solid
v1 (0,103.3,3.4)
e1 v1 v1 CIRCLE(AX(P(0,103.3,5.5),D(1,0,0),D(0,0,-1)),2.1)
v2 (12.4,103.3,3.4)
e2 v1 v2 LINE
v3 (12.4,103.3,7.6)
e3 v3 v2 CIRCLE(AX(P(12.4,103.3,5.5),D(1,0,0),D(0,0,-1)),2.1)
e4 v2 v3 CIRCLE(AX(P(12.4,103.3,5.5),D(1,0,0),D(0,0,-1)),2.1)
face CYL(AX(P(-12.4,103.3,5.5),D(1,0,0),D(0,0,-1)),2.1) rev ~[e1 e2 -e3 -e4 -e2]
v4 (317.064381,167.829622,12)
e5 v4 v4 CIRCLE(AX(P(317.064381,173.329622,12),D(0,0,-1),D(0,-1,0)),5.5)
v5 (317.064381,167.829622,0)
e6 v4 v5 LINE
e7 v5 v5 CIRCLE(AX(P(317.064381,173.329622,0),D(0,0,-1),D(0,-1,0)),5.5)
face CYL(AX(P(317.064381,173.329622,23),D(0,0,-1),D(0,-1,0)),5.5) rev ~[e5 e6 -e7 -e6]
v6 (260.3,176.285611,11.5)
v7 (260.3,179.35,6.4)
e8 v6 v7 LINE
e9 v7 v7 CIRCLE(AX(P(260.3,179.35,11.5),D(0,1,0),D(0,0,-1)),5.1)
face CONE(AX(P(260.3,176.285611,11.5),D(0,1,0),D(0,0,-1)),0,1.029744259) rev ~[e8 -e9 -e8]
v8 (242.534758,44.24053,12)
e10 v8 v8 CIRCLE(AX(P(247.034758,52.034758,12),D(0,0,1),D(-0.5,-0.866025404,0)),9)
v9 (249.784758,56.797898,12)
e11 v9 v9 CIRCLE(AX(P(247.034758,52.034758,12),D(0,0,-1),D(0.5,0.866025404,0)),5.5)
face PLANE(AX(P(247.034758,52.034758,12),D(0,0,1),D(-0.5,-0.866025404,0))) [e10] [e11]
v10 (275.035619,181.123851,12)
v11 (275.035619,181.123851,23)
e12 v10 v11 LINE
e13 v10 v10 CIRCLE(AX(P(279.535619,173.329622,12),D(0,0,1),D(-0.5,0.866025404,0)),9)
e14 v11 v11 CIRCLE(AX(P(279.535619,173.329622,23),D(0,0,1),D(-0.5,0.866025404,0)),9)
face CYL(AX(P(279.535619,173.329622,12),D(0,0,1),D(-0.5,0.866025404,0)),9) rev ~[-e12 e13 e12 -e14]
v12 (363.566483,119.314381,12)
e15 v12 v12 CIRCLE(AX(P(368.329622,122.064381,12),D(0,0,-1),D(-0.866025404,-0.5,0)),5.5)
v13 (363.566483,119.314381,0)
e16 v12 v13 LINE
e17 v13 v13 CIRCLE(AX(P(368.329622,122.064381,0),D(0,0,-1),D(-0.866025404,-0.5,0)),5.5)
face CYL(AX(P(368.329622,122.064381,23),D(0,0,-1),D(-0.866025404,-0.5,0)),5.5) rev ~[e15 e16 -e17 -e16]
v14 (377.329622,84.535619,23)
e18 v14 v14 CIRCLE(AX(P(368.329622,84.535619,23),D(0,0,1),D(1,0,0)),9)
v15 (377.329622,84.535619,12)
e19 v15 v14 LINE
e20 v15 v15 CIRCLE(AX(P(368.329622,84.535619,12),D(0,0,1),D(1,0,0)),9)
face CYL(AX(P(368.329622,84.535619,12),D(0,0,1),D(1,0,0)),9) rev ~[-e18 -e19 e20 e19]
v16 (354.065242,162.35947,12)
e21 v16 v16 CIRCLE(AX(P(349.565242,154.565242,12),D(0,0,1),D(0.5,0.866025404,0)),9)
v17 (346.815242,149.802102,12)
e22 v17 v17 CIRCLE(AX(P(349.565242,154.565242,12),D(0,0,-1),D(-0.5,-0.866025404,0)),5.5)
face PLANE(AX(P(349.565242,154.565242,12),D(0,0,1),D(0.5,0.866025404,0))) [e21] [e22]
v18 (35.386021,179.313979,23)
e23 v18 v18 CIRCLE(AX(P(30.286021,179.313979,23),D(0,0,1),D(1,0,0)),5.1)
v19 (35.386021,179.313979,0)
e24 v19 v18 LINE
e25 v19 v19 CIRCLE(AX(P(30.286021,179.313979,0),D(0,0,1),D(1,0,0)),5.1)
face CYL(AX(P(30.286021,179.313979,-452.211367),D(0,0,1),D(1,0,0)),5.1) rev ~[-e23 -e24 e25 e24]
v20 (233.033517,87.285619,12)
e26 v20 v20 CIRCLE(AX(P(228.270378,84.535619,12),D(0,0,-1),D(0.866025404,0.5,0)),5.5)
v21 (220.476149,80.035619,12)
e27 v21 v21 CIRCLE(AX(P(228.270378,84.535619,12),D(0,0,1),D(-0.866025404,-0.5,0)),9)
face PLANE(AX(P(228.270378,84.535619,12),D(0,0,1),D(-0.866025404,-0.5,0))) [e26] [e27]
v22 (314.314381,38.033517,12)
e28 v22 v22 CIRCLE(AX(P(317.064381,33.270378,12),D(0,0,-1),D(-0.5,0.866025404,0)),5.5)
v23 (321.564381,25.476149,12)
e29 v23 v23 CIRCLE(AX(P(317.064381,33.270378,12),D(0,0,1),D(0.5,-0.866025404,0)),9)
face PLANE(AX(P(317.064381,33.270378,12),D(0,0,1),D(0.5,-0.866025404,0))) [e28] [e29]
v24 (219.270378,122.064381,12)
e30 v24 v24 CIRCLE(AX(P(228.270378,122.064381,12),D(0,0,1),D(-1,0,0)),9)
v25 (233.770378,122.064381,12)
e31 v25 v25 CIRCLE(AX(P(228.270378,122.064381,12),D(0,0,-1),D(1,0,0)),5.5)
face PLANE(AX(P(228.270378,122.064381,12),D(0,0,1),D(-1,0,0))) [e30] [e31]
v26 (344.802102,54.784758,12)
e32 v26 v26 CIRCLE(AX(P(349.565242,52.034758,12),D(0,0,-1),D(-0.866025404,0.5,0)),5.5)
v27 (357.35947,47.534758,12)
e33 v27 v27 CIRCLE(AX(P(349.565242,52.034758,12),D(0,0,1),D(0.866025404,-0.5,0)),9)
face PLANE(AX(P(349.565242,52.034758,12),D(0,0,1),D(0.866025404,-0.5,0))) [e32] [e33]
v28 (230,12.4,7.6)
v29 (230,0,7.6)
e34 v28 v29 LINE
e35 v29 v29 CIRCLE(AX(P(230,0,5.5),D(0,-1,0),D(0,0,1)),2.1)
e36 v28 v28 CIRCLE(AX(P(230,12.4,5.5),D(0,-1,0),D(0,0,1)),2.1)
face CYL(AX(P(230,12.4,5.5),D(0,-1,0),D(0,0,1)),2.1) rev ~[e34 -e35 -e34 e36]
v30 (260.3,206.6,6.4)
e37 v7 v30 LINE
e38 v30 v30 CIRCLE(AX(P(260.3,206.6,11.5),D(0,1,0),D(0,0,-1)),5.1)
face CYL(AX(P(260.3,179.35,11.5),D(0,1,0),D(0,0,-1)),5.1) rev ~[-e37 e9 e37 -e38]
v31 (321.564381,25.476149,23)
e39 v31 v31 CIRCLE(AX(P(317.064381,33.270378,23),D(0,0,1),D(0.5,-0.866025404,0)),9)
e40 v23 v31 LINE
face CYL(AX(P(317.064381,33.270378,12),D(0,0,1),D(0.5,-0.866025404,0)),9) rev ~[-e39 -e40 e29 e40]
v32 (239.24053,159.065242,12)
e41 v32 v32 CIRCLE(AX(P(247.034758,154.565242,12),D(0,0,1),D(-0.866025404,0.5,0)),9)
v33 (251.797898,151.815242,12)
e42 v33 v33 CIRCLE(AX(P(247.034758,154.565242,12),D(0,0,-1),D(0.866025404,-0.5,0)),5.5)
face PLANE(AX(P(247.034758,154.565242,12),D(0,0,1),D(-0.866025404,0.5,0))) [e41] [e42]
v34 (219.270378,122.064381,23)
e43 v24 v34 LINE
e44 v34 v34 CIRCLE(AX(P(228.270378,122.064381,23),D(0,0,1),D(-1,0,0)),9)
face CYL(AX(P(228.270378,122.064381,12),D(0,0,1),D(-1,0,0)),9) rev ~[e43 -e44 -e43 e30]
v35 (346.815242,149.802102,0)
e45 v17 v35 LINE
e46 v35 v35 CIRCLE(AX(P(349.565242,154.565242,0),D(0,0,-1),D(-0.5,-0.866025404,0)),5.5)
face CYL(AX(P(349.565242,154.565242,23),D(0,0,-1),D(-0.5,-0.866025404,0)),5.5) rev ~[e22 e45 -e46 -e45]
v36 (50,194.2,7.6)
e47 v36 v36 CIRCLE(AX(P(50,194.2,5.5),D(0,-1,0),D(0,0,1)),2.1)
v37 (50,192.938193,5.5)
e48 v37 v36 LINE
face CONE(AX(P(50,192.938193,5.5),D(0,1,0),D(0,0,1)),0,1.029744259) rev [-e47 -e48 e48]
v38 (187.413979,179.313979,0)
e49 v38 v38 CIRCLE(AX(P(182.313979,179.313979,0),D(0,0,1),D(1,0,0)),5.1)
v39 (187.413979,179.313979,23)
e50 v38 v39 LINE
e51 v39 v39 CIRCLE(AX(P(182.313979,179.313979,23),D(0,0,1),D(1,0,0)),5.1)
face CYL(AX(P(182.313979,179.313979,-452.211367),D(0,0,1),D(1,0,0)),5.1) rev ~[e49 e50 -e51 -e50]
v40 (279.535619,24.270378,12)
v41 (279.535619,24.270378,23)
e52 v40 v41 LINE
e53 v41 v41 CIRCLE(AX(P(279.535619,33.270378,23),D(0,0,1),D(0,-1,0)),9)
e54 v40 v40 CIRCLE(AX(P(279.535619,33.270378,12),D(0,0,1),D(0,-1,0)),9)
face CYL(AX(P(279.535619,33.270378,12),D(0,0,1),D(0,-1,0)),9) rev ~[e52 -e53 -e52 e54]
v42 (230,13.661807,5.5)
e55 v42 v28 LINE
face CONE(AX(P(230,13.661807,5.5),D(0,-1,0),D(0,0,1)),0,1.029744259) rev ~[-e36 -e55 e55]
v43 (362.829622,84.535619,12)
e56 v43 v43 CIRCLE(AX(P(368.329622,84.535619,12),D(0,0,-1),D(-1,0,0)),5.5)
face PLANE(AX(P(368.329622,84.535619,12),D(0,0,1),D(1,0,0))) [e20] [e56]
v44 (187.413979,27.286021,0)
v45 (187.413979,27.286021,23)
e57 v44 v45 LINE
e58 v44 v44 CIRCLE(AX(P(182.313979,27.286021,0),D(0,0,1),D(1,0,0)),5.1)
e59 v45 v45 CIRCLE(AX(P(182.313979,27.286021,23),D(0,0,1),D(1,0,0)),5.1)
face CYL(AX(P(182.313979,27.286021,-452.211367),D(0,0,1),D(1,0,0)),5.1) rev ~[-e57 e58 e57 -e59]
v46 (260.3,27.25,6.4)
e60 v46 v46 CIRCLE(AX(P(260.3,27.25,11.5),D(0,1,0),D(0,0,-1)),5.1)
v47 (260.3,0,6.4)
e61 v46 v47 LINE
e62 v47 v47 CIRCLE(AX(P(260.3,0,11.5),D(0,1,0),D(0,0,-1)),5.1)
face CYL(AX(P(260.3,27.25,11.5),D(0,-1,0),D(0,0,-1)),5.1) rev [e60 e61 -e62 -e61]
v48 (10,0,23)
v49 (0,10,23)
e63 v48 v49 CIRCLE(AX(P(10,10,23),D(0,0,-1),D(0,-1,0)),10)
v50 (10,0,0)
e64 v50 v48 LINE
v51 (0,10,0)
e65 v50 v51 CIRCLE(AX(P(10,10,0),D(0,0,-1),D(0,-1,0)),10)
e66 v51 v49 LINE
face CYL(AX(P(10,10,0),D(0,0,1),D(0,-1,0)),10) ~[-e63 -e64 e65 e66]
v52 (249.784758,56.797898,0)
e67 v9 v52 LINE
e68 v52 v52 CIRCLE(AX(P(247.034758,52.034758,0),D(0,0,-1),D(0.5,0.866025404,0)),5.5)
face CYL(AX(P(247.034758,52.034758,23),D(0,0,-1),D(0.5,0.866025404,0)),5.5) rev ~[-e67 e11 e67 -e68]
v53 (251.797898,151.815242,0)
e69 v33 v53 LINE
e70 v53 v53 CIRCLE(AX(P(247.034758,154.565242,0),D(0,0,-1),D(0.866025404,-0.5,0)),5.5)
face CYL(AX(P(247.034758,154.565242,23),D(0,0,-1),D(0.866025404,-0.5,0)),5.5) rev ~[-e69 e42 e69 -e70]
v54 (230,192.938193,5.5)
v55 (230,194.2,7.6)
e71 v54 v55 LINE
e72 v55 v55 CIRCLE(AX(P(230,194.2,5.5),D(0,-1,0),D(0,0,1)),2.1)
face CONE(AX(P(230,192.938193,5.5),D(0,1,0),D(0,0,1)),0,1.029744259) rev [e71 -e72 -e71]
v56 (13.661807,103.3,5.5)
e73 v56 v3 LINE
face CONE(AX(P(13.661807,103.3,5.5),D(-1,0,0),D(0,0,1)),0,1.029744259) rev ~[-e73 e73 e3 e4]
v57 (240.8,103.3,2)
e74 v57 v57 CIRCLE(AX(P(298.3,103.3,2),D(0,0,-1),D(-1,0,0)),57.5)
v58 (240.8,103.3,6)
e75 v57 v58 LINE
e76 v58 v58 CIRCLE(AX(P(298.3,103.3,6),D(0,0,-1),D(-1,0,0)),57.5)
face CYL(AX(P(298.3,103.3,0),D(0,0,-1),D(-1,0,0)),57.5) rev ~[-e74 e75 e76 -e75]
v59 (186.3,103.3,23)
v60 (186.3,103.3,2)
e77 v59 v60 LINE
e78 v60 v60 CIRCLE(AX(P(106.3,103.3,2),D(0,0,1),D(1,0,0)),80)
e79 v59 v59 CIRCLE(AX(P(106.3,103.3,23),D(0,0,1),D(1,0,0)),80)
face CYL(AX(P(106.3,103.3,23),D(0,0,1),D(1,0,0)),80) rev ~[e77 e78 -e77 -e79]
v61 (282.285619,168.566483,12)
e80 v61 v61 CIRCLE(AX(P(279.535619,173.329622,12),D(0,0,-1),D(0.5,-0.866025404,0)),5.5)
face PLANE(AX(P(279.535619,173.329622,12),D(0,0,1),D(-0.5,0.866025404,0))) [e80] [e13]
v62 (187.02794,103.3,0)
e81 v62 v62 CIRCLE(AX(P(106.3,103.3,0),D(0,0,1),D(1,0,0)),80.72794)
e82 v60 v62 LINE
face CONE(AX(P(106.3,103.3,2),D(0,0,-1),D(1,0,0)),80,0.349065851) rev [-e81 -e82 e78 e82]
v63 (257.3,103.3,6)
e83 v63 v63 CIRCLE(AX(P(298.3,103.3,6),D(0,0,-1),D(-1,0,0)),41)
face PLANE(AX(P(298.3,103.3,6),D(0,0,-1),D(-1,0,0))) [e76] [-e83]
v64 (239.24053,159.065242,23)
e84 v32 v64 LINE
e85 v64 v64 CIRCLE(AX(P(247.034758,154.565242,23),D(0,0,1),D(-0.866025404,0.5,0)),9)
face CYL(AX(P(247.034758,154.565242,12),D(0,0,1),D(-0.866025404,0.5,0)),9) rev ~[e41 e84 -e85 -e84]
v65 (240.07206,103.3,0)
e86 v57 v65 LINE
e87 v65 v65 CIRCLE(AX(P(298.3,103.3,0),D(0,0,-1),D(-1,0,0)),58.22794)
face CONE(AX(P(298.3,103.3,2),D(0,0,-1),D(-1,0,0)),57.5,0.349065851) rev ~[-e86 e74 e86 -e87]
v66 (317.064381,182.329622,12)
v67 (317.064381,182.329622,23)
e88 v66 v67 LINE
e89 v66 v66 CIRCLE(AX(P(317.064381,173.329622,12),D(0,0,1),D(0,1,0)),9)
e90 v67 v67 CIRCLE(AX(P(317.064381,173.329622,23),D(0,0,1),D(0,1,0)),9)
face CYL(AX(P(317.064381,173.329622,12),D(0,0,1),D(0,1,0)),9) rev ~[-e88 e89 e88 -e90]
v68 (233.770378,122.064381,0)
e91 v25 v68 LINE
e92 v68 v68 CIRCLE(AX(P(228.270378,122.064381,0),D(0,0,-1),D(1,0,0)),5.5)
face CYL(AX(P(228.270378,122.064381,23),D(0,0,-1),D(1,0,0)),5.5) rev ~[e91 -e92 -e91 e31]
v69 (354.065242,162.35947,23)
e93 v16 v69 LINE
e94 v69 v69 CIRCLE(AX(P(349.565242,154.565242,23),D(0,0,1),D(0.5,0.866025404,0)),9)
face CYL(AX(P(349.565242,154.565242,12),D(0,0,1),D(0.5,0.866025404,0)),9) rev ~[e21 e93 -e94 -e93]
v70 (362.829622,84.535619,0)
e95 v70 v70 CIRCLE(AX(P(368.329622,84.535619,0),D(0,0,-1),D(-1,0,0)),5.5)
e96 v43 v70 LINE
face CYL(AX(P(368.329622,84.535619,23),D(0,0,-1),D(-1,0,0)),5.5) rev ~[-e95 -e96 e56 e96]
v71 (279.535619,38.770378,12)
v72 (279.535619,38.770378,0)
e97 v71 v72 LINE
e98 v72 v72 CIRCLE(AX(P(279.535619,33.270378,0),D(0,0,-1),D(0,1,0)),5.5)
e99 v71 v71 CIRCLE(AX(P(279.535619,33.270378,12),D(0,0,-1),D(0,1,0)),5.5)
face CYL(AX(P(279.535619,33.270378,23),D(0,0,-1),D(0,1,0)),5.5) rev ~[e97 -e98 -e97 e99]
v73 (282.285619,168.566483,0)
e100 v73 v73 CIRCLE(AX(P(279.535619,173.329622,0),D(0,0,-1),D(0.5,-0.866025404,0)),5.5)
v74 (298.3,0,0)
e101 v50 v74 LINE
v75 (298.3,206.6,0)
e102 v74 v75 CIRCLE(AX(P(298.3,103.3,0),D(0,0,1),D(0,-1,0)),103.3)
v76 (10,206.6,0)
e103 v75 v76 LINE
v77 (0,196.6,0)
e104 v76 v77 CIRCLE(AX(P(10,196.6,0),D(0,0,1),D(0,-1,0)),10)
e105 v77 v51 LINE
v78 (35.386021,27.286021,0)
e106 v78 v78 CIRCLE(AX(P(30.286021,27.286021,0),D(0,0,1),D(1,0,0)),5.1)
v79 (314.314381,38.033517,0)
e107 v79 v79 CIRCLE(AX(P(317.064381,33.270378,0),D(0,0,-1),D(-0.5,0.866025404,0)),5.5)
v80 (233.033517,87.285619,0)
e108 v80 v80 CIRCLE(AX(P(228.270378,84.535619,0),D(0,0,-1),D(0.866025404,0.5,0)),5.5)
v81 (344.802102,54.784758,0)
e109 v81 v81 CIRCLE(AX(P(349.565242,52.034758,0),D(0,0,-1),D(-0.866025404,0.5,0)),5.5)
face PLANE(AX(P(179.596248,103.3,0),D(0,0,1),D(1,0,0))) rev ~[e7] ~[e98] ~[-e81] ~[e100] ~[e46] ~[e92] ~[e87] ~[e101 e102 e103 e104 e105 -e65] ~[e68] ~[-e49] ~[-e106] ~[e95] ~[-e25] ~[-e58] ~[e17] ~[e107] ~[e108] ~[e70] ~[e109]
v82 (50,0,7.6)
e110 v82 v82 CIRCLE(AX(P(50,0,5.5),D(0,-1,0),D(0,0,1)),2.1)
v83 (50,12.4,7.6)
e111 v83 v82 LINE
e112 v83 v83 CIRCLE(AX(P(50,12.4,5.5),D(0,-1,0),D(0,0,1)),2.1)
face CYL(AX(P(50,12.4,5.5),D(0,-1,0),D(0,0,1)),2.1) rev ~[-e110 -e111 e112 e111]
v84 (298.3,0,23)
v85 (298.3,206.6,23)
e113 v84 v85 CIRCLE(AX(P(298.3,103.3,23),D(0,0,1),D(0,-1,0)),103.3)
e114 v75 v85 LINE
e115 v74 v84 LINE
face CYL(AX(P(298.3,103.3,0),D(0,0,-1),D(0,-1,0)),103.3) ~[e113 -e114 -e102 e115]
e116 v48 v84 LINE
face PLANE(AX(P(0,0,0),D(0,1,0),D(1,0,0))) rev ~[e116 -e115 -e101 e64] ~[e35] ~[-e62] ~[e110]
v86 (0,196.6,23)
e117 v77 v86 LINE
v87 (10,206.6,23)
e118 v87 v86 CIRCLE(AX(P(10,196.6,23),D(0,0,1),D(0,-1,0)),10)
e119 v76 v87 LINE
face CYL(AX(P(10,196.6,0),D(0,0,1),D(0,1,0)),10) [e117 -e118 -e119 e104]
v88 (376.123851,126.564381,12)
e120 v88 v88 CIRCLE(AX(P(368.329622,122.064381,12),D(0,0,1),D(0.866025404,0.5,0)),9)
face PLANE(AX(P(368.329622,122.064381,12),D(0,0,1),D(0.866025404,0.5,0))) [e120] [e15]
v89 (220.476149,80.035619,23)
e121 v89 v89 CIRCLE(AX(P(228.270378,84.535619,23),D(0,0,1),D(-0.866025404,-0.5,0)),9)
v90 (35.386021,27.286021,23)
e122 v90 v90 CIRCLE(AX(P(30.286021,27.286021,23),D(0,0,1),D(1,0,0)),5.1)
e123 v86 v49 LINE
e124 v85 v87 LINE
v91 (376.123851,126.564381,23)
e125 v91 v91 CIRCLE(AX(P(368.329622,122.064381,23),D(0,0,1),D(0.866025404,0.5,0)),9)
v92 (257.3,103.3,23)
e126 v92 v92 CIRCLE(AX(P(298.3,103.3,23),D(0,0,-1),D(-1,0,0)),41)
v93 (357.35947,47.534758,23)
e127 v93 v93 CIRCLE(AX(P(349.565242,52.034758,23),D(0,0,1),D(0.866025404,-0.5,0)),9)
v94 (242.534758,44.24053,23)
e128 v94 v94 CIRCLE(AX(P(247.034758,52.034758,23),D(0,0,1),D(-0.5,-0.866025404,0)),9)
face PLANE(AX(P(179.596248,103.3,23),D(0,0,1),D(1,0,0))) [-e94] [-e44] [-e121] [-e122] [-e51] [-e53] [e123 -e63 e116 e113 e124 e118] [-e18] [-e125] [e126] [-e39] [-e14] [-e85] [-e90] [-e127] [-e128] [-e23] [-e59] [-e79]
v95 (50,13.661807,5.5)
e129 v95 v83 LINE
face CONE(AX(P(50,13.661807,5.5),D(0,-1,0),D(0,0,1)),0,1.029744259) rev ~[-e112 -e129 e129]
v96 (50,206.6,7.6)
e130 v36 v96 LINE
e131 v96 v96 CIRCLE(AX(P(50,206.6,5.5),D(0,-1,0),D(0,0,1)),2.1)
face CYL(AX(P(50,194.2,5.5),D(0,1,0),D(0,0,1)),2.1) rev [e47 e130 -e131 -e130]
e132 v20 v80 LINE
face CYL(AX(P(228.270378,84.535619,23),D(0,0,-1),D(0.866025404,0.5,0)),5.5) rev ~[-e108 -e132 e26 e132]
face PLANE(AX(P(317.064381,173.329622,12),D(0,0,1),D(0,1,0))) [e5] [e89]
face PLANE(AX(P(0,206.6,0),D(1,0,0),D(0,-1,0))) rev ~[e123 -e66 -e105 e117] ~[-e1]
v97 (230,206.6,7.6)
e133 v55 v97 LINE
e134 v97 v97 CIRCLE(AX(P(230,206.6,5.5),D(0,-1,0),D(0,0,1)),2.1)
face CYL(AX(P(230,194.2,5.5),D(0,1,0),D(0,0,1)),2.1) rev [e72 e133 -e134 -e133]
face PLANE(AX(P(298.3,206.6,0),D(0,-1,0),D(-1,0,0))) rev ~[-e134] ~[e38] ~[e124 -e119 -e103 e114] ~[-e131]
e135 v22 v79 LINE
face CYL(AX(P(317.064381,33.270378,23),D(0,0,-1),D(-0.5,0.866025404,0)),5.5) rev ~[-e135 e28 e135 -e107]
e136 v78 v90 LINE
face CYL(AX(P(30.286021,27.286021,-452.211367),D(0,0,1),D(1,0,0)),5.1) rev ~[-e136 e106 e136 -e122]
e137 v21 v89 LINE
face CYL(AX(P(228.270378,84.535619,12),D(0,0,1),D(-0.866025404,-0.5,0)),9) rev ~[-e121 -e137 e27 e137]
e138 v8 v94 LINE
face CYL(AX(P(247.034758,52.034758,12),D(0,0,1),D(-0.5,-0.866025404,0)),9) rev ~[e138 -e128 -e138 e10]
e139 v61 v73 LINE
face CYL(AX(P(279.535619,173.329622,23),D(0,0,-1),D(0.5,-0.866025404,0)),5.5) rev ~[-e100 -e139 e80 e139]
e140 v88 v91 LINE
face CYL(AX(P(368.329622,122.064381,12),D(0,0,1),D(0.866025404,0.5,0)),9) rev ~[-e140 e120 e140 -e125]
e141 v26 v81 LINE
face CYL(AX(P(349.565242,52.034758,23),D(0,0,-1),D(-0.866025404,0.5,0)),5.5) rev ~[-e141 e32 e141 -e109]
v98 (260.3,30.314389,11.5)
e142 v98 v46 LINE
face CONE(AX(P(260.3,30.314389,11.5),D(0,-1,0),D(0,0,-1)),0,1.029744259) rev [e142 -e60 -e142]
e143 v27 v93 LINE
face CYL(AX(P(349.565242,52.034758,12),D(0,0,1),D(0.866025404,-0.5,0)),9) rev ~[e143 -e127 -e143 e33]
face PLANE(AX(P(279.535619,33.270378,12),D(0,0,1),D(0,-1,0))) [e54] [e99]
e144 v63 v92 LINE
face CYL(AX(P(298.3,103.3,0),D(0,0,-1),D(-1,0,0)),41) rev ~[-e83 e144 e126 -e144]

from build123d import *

# Parameters (mm, degrees)
BOSS_EXTRUDE1_DEPTH                                  = 23
FILLET1_R                                            = 10
HOLE_SIZE_PER_SOCKET_HEAD_CAP_SCREW_TYPE_D           = 11
HOLE_SIZE_PER_SOCKET_HEAD_CAP_SCREW_TYPE_CBORE_D     = 18
HOLE_SIZE_PER_SOCKET_HEAD_CAP_SCREW_TYPE_CBORE_DEPTH = 11
CIRPATTERN1_COUNT                                    = 12
SKETCH8_R                                            = 80
CUT_EXTRUDE1_DEPTH                                   = 23
SKETCH13_R                                           = 41
CUT_EXTRUDE3_DEPTH                                   = 23
SKETCH14_R                                           = 57.5
CUT_EXTRUDE4_DEPTH                                   = 6
M12_TAPPED_HOLE2_D                                   = 10.2
M5_TAPPED_HOLE1_AT_2_COUNT                           = 2
M5_TAPPED_HOLE1_AT_2_PITCH                           = 180
CHAMFER3_SIZE                                        = 2
CHAMFER3_SIZE2                                       = 0.727940469
CHAMFER4_SIZE                                        = 2
CHAMFER4_SIZE2                                       = 0.727940469
M5_TAPPED_HOLE3_D                                    = 4.2
M5_TAPPED_HOLE3_DEPTH                                = 12.4
M5_TAPPED_HOLE3_TIP                                  = 1.2618073


with BuildPart() as part:
    # Sketch1 → Boss-Extrude1 (new body)
    with BuildSketch(Plane.XY):
        with BuildLine():
            Line((0, 0), (298.3, 0))
            ThreePointArc((298.3, 0), (401.6, 103.3), (298.3, 206.6))
            Line((298.3, 206.6), (0, 206.6))
            Line((0, 206.6), (0, 0))
        make_face()
    extrude(amount=BOSS_EXTRUDE1_DEPTH)

    # Fillet1
    fillet1_edges = [part.edges().sort_by_distance(p)[0] for p in [
        (0, 206.6, 11.5),
        (0, 0, 11.5),
    ]]
    fillet(fillet1_edges, radius=FILLET1_R)

    # Hole Size per Socket Head Cap Screw Type3 (through all)
    with Locations(Plane.XY.offset(23)):
        with Locations((368.329622406, 84.53561923)):
            hole_size_per_socket_head_cap_screw_type = CounterBoreHole(HOLE_SIZE_PER_SOCKET_HEAD_CAP_SCREW_TYPE_D / 2, HOLE_SIZE_PER_SOCKET_HEAD_CAP_SCREW_TYPE_CBORE_D / 2, HOLE_SIZE_PER_SOCKET_HEAD_CAP_SCREW_TYPE_CBORE_DEPTH)

    # CirPattern1: Hole Size per Socket Head Cap Screw Type3 ×12 about axis
    cirpattern1_axis = Axis((298.3, 103.3, 0), (0, 0, 1))
    for i in range(1, CIRPATTERN1_COUNT):
        add(hole_size_per_socket_head_cap_screw_type.rotate(cirpattern1_axis, i * 360 / CIRPATTERN1_COUNT), mode=Mode.SUBTRACT)

    # Sketch8 → Cut-Extrude1 (cut)
    with BuildSketch(Plane.XY.offset(23)):
        with Locations((106.3, 103.3)):
            Circle(SKETCH8_R)
    extrude(amount=-CUT_EXTRUDE1_DEPTH, mode=Mode.SUBTRACT)

    # Sketch13 → Cut-Extrude3 (cut)
    with BuildSketch(Plane(origin=(0, 0, 0), x_dir=(-1, 0, 0), z_dir=(0, 0, -1))):
        with Locations((-298.3, 103.3)):
            Circle(SKETCH13_R)
    extrude(amount=-CUT_EXTRUDE3_DEPTH, mode=Mode.SUBTRACT)

    # Sketch14 → Cut-Extrude4 (cut)
    with BuildSketch(Plane(origin=(0, 0, 0), x_dir=(-1, 0, 0), z_dir=(0, 0, -1))):
        with Locations((-298.3, 103.3)):
            Circle(SKETCH14_R)
    extrude(amount=-CUT_EXTRUDE4_DEPTH, mode=Mode.SUBTRACT)

    # M12 Tapped Hole2 (through all)
    with Locations(Plane(origin=(0, 0, 0), x_dir=(-1, 0, 0), z_dir=(0, 0, -1))):
        with Locations((-30.286021022, 27.286021022), (-182.313978978, 27.286021022), (-30.286021022, 179.313978978), (-182.313978978, 179.313978978), (-106.3, 103.3)):
            Hole(M12_TAPPED_HOLE2_D / 2)

    # Sketch18 → M5 Tapped Hole1 (revolve, cut)
    with BuildSketch(Plane(origin=(50, 206.6, 5.5), x_dir=(0, 0, 1), z_dir=(1, 0, 0))):
        Polygon((0, 0), (0, 13.6618073), (2.1, 12.4), (2.1, 0), align=None)
    m5_tapped_hole1 = revolve(axis=Axis((50, 212.95, 5.5), (0, -1, 0)), mode=Mode.SUBTRACT)

    # M5 Tapped Hole1 at 2: M5 Tapped Hole1 ×2
    with Locations(*[(i * M5_TAPPED_HOLE1_AT_2_PITCH, 0, 0) for i in range(1, M5_TAPPED_HOLE1_AT_2_COUNT)]):
        add(m5_tapped_hole1, mode=Mode.SUBTRACT)

    # Mirror1: M5 Tapped Hole1 across plane
    add(m5_tapped_hole1.mirror(Plane.ZX.offset(103.3)), mode=Mode.SUBTRACT)

    # Mirror1 copy 1 sketch → Mirror1 copy 1 (revolve, cut)
    with BuildSketch(Plane(origin=(230, 0, 5.5), x_dir=(0, 0, 1), z_dir=(1, 0, 0))):
        Polygon((0, 0), (0, -13.6618073), (2.1, -12.4), (2.1, 0), align=None)
    revolve(axis=Axis((230, -6.35, 5.5), (0, -1, 0)), mode=Mode.SUBTRACT)

    # Chamfer3
    chamfer3_edges = [part.edges().sort_by_distance(p)[0] for p in [
        (26.3, 103.3, 0),
    ]]
    chamfer3_side = [part.faces().sort_by_distance(p)[0] for p in [
        (26.3, 103.3, 11.5),
    ]]
    chamfer(chamfer3_edges, length=CHAMFER3_SIZE, length2=CHAMFER3_SIZE2, reference=chamfer3_side[0])

    # Chamfer4
    chamfer4_edges = [part.edges().sort_by_distance(p)[0] for p in [
        (355.8, 103.3, 0),
    ]]
    chamfer4_side = [part.faces().sort_by_distance(p)[0] for p in [
        (355.8, 103.3, 3),
    ]]
    chamfer(chamfer4_edges, length=CHAMFER4_SIZE, length2=CHAMFER4_SIZE2, reference=chamfer4_side[0])

    # Sketch44 → M12 Tapped Hole3 (revolve, cut)
    with BuildSketch(Plane(origin=(260.3, 0, 11.5), x_dir=(0, 0, -1), z_dir=(1, 0, 0))):
        Polygon((0, 0), (0, 30.314389157), (5.1, 27.25), (5.1, 0), align=None)
    m12_tapped_hole3 = revolve(axis=Axis((260.3, -6.35, 11.5), (0, 1, 0)), mode=Mode.SUBTRACT)

    # Mirror5: M12 Tapped Hole3 across plane
    add(m12_tapped_hole3.mirror(Plane(origin=(0, 103.3, 0), x_dir=(0, 0, 1), z_dir=(0, -1, 0))), mode=Mode.SUBTRACT)

    # M5 Tapped Hole3
    with Locations(Plane.ZY):
        with Locations((5.5, 103.3)):
            Hole(M5_TAPPED_HOLE3_D / 2, depth=M5_TAPPED_HOLE3_DEPTH)
            with Locations((0, 0, -(M5_TAPPED_HOLE3_DEPTH + M5_TAPPED_HOLE3_TIP / 2))):  # 118° drill point
                Cone(0, M5_TAPPED_HOLE3_D / 2, M5_TAPPED_HOLE3_TIP, mode=Mode.SUBTRACT)


solid = part.part
